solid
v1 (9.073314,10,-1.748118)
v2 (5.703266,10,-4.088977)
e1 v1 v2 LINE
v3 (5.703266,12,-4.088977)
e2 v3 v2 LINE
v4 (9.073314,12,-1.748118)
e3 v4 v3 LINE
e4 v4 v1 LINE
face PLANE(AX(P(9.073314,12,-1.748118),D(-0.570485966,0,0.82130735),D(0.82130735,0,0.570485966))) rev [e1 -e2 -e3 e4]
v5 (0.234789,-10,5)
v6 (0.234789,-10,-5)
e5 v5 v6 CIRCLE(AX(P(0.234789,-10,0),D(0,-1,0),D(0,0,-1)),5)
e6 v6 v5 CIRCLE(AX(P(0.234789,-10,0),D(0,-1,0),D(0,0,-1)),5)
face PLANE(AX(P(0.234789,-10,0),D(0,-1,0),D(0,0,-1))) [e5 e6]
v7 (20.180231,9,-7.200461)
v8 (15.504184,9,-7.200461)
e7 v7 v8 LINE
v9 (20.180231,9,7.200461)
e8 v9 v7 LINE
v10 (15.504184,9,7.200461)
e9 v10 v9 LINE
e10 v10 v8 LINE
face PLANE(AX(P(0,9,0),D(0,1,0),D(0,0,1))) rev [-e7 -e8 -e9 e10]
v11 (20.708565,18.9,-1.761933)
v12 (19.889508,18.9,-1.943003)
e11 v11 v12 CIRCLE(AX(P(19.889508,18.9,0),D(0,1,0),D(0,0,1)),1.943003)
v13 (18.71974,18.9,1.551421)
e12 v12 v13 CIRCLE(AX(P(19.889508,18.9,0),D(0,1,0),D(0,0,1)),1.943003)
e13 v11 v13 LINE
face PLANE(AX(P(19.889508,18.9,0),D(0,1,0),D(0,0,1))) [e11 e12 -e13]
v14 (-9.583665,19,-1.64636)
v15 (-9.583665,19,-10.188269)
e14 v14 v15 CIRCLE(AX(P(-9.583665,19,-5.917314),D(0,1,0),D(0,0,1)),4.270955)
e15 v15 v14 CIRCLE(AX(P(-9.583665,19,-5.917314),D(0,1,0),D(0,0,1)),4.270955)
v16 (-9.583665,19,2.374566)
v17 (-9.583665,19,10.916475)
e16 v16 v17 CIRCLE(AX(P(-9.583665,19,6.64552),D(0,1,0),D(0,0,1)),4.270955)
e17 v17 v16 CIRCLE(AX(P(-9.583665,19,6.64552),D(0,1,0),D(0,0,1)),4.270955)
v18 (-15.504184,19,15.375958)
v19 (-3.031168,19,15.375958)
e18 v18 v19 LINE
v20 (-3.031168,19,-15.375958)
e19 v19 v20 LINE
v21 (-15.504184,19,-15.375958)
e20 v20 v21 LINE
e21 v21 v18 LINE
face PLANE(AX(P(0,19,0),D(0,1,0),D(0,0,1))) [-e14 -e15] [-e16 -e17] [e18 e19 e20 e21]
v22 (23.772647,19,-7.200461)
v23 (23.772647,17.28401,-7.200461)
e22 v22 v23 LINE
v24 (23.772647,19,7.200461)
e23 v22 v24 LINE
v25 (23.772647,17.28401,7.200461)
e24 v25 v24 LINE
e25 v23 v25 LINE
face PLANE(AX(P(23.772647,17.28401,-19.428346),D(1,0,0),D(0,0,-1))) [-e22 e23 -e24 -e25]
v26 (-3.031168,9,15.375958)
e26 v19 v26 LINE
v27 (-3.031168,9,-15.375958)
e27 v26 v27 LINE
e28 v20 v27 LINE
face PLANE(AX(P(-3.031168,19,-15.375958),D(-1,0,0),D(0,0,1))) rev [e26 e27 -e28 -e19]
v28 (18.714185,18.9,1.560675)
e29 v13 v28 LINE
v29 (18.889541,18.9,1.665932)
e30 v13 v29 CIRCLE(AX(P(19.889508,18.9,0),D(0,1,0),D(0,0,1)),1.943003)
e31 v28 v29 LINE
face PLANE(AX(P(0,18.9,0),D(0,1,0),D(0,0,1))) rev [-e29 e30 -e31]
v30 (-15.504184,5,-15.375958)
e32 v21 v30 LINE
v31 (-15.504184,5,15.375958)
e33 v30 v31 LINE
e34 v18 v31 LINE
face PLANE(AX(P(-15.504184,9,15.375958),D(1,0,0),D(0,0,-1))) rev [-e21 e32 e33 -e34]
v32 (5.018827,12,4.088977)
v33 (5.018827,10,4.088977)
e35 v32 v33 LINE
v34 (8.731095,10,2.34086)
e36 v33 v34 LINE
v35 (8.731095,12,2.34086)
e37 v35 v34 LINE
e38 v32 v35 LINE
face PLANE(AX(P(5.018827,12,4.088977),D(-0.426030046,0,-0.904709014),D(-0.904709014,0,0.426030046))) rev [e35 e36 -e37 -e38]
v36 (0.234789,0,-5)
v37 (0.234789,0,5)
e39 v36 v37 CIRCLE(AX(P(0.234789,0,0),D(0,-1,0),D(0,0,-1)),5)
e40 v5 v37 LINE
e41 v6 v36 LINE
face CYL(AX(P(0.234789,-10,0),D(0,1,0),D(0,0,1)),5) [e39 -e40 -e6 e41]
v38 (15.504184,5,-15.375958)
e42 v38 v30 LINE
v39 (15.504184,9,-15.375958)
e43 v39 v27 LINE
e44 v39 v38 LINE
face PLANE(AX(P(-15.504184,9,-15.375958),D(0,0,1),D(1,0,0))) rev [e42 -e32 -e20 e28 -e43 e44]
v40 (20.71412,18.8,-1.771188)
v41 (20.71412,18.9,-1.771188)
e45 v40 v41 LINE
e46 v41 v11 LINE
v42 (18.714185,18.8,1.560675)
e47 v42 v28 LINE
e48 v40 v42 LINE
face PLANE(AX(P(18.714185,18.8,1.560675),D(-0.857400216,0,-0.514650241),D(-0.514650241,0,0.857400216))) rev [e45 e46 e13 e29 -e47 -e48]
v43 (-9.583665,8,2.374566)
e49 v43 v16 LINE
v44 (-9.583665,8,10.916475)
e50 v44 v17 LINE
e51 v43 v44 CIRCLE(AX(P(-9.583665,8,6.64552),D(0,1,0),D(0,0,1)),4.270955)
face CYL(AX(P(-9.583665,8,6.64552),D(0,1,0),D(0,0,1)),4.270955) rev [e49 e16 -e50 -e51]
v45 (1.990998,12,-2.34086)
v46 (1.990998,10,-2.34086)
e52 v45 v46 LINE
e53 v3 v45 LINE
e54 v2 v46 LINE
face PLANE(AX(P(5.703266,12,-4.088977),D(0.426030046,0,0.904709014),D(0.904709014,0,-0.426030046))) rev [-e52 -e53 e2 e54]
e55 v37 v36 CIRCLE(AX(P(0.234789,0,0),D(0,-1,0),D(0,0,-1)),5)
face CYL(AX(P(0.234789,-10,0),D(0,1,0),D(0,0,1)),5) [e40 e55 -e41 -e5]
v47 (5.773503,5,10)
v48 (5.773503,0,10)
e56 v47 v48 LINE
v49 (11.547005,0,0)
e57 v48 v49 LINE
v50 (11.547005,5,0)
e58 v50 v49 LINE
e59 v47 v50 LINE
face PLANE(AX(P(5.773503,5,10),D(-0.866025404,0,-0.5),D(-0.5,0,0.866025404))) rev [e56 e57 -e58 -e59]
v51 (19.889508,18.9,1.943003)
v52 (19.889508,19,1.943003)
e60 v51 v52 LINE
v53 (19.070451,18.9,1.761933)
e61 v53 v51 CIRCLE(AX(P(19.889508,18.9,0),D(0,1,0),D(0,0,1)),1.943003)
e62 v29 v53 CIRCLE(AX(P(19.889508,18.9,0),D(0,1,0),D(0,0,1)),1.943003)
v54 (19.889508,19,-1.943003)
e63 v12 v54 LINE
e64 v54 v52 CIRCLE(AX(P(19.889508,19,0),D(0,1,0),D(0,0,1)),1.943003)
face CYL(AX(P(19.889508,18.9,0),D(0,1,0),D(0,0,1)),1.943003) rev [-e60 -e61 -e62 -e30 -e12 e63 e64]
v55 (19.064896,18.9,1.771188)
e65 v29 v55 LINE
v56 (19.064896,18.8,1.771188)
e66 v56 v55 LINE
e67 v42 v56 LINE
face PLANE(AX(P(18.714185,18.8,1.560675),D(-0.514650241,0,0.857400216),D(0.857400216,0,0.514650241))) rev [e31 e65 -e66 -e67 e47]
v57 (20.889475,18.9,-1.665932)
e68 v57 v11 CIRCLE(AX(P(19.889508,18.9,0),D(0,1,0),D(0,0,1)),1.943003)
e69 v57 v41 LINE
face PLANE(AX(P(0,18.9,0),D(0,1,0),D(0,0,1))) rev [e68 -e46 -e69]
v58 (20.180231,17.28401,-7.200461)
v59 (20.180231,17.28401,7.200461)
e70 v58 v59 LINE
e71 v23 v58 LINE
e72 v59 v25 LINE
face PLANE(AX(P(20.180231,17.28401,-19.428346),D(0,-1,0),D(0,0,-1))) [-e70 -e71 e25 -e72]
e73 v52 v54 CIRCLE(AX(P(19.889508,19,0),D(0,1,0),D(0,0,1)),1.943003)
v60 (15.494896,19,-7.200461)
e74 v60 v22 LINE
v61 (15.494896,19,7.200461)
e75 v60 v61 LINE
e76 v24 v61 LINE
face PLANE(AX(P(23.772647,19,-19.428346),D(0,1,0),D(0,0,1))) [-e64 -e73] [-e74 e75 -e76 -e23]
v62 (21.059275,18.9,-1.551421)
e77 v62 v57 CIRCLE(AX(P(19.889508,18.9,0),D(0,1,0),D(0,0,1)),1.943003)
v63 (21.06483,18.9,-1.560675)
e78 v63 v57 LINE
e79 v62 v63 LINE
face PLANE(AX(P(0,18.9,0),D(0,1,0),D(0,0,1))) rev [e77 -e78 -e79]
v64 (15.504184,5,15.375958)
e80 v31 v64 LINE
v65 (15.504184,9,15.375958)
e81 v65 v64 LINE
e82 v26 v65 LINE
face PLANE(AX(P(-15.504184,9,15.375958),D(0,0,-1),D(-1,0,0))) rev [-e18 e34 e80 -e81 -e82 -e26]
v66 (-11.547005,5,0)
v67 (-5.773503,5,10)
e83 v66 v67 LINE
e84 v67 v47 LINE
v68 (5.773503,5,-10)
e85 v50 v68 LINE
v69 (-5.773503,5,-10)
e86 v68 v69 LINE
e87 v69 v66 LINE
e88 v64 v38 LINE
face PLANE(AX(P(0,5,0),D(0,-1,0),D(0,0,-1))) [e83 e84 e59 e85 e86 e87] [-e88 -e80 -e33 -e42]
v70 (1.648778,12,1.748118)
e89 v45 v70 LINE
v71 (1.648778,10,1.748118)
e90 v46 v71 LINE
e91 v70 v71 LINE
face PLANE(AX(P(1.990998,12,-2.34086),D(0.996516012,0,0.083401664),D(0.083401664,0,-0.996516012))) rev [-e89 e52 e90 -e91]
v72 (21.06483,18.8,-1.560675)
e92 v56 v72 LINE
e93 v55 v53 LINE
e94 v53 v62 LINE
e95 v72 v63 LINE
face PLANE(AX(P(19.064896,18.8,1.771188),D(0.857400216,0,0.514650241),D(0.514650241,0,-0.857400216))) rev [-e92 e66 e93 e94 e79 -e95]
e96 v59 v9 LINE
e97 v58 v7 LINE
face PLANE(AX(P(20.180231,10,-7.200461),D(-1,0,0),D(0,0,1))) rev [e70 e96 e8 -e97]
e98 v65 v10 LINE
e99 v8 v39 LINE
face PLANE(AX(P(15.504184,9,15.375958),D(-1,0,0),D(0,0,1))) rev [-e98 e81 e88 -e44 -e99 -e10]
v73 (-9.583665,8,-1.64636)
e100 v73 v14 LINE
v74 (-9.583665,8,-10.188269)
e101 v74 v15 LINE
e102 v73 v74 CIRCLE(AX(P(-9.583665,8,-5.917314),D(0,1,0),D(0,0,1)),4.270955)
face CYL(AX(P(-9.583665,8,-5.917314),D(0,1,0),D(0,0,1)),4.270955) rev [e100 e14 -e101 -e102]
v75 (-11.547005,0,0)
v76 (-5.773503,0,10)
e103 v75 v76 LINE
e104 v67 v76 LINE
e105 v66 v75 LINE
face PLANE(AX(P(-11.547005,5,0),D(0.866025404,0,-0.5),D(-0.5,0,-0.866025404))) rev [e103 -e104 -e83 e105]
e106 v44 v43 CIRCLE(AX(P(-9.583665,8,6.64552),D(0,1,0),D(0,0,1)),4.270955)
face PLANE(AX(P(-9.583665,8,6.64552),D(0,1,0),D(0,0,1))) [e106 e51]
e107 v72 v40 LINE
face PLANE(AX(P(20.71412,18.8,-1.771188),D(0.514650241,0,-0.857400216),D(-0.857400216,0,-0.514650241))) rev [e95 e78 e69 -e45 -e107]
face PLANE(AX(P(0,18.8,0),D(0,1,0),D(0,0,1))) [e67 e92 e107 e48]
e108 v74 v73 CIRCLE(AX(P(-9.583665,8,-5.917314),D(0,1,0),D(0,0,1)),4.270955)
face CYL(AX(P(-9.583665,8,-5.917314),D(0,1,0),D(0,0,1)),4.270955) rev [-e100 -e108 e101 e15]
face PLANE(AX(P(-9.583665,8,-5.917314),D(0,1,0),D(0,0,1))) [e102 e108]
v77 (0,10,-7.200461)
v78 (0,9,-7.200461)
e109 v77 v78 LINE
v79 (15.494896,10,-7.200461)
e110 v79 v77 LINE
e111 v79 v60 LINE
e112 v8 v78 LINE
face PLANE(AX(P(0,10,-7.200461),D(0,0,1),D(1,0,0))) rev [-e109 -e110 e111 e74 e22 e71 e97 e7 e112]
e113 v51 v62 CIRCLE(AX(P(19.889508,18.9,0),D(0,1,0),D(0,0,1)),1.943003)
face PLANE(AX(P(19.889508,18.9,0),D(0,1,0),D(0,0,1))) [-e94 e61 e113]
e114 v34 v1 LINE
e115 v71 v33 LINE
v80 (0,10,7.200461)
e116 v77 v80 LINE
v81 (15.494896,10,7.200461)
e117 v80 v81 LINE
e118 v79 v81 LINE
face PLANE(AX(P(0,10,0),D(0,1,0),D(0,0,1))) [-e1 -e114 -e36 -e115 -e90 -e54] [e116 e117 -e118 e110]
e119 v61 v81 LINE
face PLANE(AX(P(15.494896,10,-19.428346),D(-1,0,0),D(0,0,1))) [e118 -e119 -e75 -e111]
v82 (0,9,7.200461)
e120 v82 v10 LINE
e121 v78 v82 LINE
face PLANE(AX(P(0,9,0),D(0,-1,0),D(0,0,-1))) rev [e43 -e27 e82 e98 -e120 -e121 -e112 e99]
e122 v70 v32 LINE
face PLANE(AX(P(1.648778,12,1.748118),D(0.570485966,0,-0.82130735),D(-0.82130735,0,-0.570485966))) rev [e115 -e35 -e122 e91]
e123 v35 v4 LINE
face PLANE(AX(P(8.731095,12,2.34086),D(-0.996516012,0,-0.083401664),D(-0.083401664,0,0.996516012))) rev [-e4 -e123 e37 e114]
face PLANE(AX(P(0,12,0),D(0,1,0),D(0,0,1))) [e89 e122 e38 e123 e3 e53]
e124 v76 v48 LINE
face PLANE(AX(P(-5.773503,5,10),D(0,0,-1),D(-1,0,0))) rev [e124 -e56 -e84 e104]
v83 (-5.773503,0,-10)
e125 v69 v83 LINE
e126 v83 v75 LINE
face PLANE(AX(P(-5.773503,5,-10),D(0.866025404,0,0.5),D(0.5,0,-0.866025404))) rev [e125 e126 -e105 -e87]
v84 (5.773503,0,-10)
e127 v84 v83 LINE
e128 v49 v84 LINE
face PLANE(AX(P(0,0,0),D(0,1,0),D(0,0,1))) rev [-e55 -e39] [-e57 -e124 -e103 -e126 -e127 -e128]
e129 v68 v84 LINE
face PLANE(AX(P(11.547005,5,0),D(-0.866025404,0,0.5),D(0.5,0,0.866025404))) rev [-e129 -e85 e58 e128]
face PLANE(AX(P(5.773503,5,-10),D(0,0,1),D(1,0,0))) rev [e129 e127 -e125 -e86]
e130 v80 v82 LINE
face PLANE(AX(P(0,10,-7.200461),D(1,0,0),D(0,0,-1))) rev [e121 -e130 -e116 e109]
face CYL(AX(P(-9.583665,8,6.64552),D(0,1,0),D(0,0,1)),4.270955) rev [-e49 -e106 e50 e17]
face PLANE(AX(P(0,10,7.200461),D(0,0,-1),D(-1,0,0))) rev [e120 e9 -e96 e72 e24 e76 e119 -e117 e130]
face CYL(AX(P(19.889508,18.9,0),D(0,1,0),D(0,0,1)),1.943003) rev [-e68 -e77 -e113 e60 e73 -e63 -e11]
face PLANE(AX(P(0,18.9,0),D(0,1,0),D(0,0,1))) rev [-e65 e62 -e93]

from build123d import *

# Parameters (mm, degrees)
BOSS_EXTRUDE1_DEPTH = 5
SKETCH2_R           = 5
BOSS_EXTRUDE2_DEPTH = 10
SKETCH3_W           = 31.008368254
SKETCH3_H           = 30.751916894
BOSS_EXTRUDE3_DEPTH = 4
SKETCH4_W           = 12.473016313
SKETCH4_H           = 30.751916894
BOSS_EXTRUDE4_DEPTH = 10
SKETCH5_W           = 20.18023145
SKETCH5_H           = 14.400921404
BOSS_EXTRUDE5_DEPTH = 1
BOSS_EXTRUDE6_DEPTH = 14.400921404
SKETCH7_R           = 4.270954595
CUT_EXTRUDE1_DEPTH  = 11
SKETCH8_R           = 1.943003429
CUT_EXTRUDE2_DEPTH  = 0.1
CUT_EXTRUDE3_DEPTH  = 0.1
BOSS_EXTRUDE7_DEPTH = 2


with BuildPart() as part:
    # Sketch1 → Boss-Extrude1 (new body)
    with BuildSketch(Plane(origin=(0, 0, 0), x_dir=(1, 0, 0), z_dir=(0, 1, 0))):
        Polygon((5.773502692, 10), (-5.773502692, 10), (-11.547005384, 0), (-5.773502692, -10), (5.773502692, -10), (11.547005384, 0), align=None)
    extrude(amount=BOSS_EXTRUDE1_DEPTH)

    # Sketch2 → Boss-Extrude2 (add)
    with BuildSketch(Plane.XZ):
        with Locations(Location((0.234789437, 0, 0), (0, 0, 270))):
            Circle(SKETCH2_R)
    extrude(amount=BOSS_EXTRUDE2_DEPTH)

    # Sketch3 → Boss-Extrude3 (add)
    with BuildSketch(Plane(origin=(0, 5, 0), x_dir=(1, 0, 0), z_dir=(0, 1, 0))):
        Rectangle(SKETCH3_W, SKETCH3_H)
    extrude(amount=BOSS_EXTRUDE3_DEPTH)

    # Sketch4 → Boss-Extrude4 (add)
    with BuildSketch(Plane(origin=(0, 9, 0), x_dir=(1, 0, 0), z_dir=(0, 1, 0))):
        with Locations((-9.267675971, 0)):
            Rectangle(SKETCH4_W, SKETCH4_H)
    extrude(amount=BOSS_EXTRUDE4_DEPTH)

    # Sketch5 → Boss-Extrude5 (add)
    with BuildSketch(Plane(origin=(0, 9, 0), x_dir=(1, 0, 0), z_dir=(0, 1, 0))):
        with Locations((10.090115725, 0)):
            Rectangle(SKETCH5_W, SKETCH5_H)
    extrude(amount=BOSS_EXTRUDE5_DEPTH)

    # Sketch6 → Boss-Extrude6 (add)
    with BuildSketch(Plane.XY.offset(7.200460702)):
        Polygon((20.18023145, 10), (20.18023145, 17.284010358), (23.772647306, 17.284010358), (23.772647306, 19), (15.494895542, 19), (15.494895542, 10), align=None)
    extrude(amount=-BOSS_EXTRUDE6_DEPTH)

    # Sketch7 → Cut-Extrude1 (cut)
    with BuildSketch(Plane(origin=(0, 19, 0), x_dir=(1, 0, 0), z_dir=(0, 1, 0))):
        with Locations(Location((-9.583665468, 5.917314438, 0), (0, 0, 270))):
            Circle(SKETCH7_R)
        with Locations(Location((-9.583665468, -6.64552011, 0), (0, 0, 270))):
            Circle(SKETCH7_R)
    extrude(amount=-CUT_EXTRUDE1_DEPTH, mode=Mode.SUBTRACT)

    # Sketch8 → Cut-Extrude2 (cut)
    with BuildSketch(Plane(origin=(0, 19, 0), x_dir=(1, 0, 0), z_dir=(0, 1, 0))):
        with Locations(Location((19.889507686, 0, 0), (0, 0, 270))):
            Circle(SKETCH8_R)
    extrude(amount=-CUT_EXTRUDE2_DEPTH, mode=Mode.SUBTRACT)

    # Sketch9 → Cut-Extrude3 (cut)
    with BuildSketch(Plane(origin=(0, 18.9, 0), x_dir=(1, 0, 0), z_dir=(0, 1, 0))):
        Polygon((18.714185293, -1.560675462), (20.714119659, 1.771187657), (21.064830078, 1.560675462), (19.064895713, -1.771187657), align=None)
    extrude(amount=-CUT_EXTRUDE3_DEPTH, mode=Mode.SUBTRACT)

    # Sketch10 → Boss-Extrude7 (add)
    with BuildSketch(Plane(origin=(0, 10, 0), x_dir=(1, 0, 0), z_dir=(0, 1, 0))):
        Polygon((5.703266191, 4.088977096), (1.990998258, 2.340859575), (1.648778474, -1.748117521), (5.018826623, -4.088977096), (8.731094556, -2.340859575), (9.07331434, 1.748117521), align=None)
    extrude(amount=BOSS_EXTRUDE7_DEPTH)


solid = part.part
